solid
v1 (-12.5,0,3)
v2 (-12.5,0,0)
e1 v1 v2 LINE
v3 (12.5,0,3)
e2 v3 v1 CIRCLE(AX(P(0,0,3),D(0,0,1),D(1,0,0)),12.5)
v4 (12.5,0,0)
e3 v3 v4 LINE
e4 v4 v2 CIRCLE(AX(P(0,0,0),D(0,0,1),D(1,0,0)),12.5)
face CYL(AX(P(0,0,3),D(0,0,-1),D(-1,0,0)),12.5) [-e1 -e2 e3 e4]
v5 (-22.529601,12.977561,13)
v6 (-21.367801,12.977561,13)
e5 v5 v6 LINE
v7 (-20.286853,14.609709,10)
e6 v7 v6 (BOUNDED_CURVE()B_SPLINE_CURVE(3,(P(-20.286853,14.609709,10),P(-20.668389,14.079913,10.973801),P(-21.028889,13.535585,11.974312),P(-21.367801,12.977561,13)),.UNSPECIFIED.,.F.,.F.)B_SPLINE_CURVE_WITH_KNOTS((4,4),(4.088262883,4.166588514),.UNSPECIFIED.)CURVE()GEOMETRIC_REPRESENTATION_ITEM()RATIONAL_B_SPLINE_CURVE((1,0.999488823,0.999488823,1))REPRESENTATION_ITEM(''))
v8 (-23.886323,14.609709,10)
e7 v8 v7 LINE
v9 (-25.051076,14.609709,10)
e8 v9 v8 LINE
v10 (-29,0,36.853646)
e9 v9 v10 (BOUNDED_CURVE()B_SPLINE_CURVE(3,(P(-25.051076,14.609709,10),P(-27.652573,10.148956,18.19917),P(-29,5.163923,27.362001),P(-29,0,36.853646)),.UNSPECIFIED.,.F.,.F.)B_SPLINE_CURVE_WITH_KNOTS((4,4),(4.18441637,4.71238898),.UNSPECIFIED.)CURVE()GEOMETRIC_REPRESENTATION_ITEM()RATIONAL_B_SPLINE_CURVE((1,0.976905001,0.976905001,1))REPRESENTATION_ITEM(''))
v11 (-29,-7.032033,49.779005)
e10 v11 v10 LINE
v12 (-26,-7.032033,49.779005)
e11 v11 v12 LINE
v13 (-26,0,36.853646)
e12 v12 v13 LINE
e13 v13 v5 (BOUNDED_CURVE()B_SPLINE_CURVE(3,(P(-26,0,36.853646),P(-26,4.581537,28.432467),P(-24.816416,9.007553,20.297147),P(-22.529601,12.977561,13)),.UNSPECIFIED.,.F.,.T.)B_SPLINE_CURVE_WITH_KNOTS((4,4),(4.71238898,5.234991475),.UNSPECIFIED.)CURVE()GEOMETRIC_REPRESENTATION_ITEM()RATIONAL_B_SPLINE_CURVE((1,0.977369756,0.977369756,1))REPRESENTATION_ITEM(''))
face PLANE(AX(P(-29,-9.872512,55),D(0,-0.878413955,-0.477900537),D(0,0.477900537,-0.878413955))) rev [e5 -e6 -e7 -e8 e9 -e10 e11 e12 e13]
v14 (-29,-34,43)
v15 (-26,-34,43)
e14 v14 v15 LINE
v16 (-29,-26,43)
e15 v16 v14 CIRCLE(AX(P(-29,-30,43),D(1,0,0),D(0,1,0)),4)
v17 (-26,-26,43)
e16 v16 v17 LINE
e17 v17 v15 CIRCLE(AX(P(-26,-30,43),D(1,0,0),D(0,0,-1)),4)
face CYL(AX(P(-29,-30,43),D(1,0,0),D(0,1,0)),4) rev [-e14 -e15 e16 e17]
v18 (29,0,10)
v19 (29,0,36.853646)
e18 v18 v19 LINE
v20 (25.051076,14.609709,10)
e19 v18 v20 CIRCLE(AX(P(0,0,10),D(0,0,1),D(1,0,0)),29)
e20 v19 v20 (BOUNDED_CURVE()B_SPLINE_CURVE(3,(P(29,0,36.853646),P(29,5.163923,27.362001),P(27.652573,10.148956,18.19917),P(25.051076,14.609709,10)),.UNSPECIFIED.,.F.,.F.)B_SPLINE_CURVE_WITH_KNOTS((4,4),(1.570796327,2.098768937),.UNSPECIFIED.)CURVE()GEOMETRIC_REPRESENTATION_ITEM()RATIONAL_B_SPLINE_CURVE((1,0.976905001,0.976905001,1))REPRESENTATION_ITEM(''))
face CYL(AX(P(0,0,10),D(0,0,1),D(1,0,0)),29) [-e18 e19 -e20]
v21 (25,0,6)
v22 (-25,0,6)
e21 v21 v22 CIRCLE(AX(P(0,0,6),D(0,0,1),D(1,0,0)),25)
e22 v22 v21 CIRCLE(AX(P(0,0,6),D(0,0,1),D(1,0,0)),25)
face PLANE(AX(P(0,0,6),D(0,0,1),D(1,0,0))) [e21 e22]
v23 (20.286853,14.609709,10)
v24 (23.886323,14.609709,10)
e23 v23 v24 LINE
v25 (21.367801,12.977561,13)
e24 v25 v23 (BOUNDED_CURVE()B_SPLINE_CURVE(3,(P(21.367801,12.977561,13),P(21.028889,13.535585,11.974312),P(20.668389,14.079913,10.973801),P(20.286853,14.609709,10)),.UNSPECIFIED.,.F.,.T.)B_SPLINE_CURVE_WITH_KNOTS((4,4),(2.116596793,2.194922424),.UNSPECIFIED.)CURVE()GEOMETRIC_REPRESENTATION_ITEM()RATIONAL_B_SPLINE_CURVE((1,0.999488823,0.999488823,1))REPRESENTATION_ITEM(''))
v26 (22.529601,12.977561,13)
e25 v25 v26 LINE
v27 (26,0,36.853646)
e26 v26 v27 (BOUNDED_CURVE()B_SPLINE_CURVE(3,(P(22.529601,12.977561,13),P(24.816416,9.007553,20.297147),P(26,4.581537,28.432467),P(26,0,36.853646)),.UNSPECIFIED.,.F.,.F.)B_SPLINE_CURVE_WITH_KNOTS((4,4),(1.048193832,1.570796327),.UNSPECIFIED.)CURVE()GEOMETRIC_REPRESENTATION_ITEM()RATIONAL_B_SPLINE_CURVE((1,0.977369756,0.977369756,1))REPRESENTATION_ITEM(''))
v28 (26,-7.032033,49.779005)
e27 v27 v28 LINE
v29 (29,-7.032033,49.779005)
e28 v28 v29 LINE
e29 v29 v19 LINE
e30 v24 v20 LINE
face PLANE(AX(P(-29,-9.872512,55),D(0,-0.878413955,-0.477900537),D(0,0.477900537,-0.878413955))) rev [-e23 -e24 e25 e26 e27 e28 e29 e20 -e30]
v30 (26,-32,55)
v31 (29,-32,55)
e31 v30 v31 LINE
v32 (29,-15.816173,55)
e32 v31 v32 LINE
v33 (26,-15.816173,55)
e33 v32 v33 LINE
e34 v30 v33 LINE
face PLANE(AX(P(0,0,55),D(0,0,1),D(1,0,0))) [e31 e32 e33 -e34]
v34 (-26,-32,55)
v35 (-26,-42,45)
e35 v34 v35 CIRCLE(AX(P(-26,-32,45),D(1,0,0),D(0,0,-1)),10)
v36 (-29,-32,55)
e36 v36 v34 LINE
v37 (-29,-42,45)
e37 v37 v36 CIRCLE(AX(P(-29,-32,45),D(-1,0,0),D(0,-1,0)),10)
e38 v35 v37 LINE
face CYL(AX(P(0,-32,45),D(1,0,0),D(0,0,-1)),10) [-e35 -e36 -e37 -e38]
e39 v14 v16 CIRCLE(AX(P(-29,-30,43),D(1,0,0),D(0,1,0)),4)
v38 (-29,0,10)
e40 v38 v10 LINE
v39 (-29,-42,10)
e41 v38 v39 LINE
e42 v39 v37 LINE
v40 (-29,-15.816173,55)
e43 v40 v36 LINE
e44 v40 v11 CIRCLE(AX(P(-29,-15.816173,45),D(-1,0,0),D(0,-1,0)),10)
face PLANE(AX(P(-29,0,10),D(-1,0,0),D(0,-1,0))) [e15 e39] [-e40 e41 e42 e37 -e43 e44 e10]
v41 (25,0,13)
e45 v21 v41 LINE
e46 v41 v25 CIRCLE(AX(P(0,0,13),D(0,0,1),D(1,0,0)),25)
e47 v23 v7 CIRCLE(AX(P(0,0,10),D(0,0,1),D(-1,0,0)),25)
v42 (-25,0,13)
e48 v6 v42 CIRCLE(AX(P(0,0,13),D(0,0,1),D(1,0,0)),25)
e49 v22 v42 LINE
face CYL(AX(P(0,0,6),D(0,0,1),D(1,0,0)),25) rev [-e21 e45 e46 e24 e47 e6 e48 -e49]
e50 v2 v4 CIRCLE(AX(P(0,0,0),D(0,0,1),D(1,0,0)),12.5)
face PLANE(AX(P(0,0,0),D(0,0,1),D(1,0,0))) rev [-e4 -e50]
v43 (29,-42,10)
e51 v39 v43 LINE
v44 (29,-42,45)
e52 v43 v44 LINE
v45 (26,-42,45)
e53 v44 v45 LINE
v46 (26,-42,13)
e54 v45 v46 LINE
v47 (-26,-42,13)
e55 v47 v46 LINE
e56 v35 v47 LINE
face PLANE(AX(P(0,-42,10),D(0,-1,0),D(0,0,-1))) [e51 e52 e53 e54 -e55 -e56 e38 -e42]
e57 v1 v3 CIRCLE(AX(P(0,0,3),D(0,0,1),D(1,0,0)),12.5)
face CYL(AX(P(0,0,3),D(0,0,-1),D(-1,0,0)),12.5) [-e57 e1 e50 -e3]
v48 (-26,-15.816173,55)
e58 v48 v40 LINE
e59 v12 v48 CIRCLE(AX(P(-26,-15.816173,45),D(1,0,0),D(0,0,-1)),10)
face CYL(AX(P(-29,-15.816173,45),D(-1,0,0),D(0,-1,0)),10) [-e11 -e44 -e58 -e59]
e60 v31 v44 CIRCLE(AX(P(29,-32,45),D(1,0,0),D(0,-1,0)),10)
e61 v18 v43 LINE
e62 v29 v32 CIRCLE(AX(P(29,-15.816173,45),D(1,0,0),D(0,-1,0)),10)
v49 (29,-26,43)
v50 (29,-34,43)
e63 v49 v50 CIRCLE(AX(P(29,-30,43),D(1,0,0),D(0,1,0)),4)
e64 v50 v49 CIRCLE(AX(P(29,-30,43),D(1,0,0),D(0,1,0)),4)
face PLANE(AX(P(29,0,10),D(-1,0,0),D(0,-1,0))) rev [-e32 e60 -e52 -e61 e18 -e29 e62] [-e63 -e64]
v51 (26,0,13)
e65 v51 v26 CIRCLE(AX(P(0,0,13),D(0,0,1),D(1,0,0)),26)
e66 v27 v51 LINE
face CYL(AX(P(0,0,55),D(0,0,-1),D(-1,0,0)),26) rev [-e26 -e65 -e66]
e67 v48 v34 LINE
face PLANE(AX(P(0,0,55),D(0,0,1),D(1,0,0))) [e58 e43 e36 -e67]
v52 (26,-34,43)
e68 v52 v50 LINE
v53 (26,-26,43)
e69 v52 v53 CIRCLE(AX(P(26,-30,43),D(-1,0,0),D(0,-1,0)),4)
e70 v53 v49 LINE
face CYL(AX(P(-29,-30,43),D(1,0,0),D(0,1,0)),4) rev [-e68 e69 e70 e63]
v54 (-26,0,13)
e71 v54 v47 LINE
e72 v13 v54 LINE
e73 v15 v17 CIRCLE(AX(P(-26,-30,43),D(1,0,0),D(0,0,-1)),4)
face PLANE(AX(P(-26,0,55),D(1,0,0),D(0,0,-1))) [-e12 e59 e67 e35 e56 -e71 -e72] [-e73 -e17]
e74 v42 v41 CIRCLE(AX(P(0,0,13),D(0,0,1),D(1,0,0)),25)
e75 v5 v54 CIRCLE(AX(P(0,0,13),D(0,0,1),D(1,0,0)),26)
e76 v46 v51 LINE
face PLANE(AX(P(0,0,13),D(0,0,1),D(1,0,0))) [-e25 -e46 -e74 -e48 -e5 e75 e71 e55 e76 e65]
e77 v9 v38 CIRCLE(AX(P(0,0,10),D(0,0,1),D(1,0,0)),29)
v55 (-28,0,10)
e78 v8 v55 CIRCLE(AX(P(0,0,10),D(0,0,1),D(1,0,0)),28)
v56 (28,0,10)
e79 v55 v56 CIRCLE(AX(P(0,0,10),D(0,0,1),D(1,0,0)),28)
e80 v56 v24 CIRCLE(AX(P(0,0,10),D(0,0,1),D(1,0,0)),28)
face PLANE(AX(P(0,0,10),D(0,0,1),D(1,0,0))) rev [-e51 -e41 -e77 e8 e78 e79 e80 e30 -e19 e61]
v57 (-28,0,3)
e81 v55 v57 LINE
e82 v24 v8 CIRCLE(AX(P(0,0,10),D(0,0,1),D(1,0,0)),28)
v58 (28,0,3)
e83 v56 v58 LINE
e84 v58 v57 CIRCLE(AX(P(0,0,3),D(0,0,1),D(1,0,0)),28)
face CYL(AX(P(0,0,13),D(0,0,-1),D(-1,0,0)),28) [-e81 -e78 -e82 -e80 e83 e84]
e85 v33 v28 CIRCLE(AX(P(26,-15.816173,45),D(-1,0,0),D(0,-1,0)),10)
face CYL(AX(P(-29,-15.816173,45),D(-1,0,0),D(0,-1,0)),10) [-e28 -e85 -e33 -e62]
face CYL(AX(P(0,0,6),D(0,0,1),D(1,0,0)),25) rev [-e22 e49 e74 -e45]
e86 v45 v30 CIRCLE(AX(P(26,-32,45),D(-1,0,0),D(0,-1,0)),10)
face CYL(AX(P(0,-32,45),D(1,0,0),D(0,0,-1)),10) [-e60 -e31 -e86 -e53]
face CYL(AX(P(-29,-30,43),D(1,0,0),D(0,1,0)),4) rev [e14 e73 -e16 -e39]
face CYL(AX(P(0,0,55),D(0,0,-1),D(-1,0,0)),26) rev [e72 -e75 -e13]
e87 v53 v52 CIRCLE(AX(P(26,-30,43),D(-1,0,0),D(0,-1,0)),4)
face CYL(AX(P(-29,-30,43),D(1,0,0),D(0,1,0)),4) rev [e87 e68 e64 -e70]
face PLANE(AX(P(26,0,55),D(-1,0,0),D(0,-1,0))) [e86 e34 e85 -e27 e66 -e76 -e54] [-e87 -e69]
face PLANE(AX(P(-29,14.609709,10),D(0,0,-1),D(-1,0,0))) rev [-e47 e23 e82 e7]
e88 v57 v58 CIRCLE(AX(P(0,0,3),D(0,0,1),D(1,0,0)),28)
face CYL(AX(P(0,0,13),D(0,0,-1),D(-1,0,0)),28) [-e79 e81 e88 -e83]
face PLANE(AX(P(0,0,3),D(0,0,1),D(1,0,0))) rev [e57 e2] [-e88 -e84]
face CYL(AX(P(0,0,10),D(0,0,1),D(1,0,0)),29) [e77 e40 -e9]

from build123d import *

# Parameters (mm, degrees)
SKETCH_1_R          = 12.5
EXTRUDE_1_DEPTH     = 3
SKETCH_2_R          = 28
EXTRUDE_2_DEPTH     = 10
SKETCH_3_R          = 25
CUT_EXTRUDE_1_DEPTH = 7
SKETCH_6_R          = 29
SKETCH_6_R_2        = 25
EXTRUDE_4_DEPTH     = 3
EXTRUDE_3_DEPTH     = 3
EXTRUDE_START       = 42
EXTRUDE_5_DEPTH     = 42
CUT_EXTRUDE_2_DEPTH = 91.293964361
FILLET_1_R          = 10
SKETCH_9_R          = 4
CUT_EXTRUDE_4_DEPTH = 91.293964361


with BuildPart() as part:
    # 草图1 → 凸台-拉伸1 (new body)
    with BuildSketch(Plane.XY):
        Circle(SKETCH_1_R)
    extrude(amount=EXTRUDE_1_DEPTH)

    # 草图2 → 凸台-拉伸2 (add)
    with BuildSketch(Plane.XY.offset(3)):
        Circle(SKETCH_2_R)
    extrude(amount=EXTRUDE_2_DEPTH)

    # 草图3 → 切除-拉伸1 (cut)
    with BuildSketch(Plane.XY.offset(13)):
        Circle(SKETCH_3_R)
    extrude(amount=-CUT_EXTRUDE_1_DEPTH, mode=Mode.SUBTRACT)

    # 草图6 → 凸台-拉伸4 (add)
    with BuildSketch(Plane.XY.offset(13)):
        Circle(SKETCH_6_R)
        Circle(SKETCH_6_R_2, mode=Mode.SUBTRACT)
    extrude(amount=-EXTRUDE_4_DEPTH)

    # 草图4 → 凸台-拉伸3 (add)
    with BuildSketch(Plane.XY.offset(13)):
        with BuildLine():
            ThreePointArc((29, 0), (0, -29), (-29, 0))
            Line((-29, 0), (-29, -42))
            Line((-29, -42), (29, -42))
            Line((29, -42), (29, 0))
        make_face()
    extrude(amount=-EXTRUDE_3_DEPTH)

    # 草图7 → 凸台-拉伸5 (add)
    with BuildSketch(Plane.XY.offset(13).offset(EXTRUDE_START)):
        with BuildLine():
            Line((-26, -42), (-26, 0))
            ThreePointArc((-26, 0), (0, 26), (26, 0))
            Line((26, 0), (26, -42))
            Line((26, -42), (29, -42))
            Line((29, -42), (29, 0))
            ThreePointArc((29, 0), (0, 29), (-29, 0))
            Line((-29, 0), (-29, -42))
            Line((-29, -42), (-26, -42))
        make_face()
    extrude(amount=-EXTRUDE_5_DEPTH)

    # 草图8 → 切除-拉伸2 (cut, through all)
    with BuildSketch(Plane(origin=(29, 0, 0), x_dir=(0, 0, -1), z_dir=(1, 0, 0))):
        Polygon((-55, -9.872511864), (-10, 14.609708665), (-10, 29), (-55, 29), align=None)
    extrude(amount=-CUT_EXTRUDE_2_DEPTH, mode=Mode.SUBTRACT)

    # 圆角1
    fillet_1_edges = [part.edges().sort_by_distance(p)[0] for p in [
        (27.5, -9.872511864, 55),
        (27.5, -42, 55),
        (-27.5, -9.872511864, 55),
        (-27.5, -42, 55),
    ]]
    fillet(fillet_1_edges, radius=FILLET_1_R)

    # 草图9 → 切除-拉伸4 (cut, through all)
    with BuildSketch(Plane(origin=(29, 0, 0), x_dir=(0, 0, -1), z_dir=(1, 0, 0))):
        with Locations(Location((-43, -30, 0), (0, 0, 90))):
            Circle(SKETCH_9_R)
    extrude(amount=-CUT_EXTRUDE_4_DEPTH, mode=Mode.SUBTRACT)


solid = part.part
